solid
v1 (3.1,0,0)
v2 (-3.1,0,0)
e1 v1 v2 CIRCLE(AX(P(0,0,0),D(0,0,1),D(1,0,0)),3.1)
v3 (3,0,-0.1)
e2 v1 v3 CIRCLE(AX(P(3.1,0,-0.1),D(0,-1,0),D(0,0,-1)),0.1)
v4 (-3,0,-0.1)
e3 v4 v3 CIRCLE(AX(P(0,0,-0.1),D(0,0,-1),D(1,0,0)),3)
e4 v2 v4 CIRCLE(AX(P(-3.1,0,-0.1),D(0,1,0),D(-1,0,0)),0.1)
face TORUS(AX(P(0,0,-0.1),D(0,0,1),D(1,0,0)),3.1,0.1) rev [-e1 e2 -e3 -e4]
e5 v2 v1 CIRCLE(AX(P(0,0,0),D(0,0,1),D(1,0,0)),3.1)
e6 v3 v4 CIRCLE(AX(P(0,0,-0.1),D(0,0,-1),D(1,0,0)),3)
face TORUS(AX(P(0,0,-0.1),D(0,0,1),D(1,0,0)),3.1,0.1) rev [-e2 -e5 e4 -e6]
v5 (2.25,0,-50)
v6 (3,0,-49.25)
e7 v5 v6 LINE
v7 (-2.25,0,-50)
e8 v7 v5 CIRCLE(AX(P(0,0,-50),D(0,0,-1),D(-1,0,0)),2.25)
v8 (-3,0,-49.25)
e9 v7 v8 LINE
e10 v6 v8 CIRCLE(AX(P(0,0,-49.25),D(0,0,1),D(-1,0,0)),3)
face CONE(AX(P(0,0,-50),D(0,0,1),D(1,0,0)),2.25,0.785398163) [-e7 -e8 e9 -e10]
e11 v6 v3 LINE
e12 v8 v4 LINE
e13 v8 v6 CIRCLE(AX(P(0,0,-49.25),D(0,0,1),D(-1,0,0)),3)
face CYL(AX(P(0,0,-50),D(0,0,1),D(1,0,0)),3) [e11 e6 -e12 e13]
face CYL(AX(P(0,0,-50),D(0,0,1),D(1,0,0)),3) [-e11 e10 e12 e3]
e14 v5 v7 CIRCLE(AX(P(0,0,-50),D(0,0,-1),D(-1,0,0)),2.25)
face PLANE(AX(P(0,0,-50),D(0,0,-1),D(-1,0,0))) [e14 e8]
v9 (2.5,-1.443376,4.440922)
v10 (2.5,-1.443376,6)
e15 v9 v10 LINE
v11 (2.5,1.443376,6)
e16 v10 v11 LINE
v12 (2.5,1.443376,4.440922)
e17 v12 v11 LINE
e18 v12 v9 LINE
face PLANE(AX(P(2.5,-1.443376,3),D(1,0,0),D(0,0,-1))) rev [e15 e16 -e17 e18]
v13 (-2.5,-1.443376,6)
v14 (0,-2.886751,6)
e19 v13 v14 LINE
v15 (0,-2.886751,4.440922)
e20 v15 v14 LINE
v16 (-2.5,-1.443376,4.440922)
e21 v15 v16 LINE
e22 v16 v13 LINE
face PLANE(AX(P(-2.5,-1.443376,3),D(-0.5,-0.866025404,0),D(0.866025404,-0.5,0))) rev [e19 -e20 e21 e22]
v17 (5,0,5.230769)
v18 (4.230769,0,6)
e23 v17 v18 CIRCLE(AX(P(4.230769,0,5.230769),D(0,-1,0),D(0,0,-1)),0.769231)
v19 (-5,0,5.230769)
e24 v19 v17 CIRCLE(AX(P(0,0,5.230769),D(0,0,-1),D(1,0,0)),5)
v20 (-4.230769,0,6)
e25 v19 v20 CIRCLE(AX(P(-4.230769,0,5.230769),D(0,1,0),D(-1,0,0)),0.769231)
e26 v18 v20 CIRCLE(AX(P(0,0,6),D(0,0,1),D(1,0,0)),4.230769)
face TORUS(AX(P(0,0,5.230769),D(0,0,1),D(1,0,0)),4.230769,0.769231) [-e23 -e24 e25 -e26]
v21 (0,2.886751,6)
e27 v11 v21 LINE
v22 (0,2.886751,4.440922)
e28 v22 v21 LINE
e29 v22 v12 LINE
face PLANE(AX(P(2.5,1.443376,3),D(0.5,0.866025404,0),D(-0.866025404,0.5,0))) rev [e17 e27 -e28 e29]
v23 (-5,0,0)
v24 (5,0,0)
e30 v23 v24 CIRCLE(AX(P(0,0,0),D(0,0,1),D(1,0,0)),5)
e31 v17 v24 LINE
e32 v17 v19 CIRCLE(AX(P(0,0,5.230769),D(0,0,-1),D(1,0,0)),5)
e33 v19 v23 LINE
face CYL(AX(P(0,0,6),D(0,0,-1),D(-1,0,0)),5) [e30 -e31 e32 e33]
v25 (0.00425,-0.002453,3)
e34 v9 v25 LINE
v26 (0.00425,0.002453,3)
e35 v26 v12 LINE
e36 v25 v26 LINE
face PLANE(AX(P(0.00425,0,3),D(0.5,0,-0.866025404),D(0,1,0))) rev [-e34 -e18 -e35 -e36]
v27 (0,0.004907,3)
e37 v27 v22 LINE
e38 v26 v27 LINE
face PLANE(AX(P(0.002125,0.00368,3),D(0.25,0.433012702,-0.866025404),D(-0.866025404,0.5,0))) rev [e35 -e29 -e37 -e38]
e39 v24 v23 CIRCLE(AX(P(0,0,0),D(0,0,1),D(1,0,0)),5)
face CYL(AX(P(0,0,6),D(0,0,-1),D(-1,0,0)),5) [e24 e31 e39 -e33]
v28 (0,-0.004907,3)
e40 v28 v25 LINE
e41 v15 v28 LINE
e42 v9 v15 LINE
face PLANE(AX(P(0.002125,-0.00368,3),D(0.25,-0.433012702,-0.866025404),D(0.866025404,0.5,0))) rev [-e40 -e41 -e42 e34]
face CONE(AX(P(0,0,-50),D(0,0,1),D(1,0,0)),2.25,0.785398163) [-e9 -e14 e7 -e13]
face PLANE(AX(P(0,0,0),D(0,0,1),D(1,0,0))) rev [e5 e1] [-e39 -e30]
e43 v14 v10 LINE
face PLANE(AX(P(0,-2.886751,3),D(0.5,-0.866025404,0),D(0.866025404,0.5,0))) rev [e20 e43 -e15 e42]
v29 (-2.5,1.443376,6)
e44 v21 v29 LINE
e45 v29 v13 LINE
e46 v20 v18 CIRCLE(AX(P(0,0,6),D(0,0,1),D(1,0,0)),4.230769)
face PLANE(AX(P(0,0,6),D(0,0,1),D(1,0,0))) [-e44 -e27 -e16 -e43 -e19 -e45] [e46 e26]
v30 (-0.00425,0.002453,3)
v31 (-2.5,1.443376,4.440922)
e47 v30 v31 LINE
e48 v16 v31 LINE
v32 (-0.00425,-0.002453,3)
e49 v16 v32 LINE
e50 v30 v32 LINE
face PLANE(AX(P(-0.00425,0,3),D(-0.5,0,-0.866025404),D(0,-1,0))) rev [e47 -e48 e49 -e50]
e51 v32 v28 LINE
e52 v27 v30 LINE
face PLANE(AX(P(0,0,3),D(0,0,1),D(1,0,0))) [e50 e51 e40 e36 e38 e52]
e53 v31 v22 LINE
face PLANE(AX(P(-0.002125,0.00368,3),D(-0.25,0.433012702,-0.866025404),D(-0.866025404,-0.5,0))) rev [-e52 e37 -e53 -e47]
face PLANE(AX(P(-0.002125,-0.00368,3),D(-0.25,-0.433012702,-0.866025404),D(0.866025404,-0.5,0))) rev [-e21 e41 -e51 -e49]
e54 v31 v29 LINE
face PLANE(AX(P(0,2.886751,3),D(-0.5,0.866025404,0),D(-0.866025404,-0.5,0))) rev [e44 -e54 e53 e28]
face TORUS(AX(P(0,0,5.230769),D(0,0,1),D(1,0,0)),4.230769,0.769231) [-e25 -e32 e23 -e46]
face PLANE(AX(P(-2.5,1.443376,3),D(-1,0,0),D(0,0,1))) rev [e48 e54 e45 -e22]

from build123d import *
from OCP.BRepFilletAPI import BRepFilletAPI_MakeChamfer

# Parameters (mm, degrees)
SKETCH1_R           = 5
BOSS_EXTRUDE1_DEPTH = 6
CUT_EXTRUDE1_DEPTH  = 3
SKETCH3_R           = 3
BOSS_EXTRUDE2_DEPTH = 50
CHAMFER1_SIZE       = 0.75
FILLET1_R           = 0.769230769
CHAMFER2_SIZE       = 1.44092219
CHAMFER2_SIZE2      = 2.495750443
FILLET2_R           = 0.1


with BuildPart() as part:
    # Sketch1 → Boss-Extrude1 (new body)
    with BuildSketch(Plane.XY):
        Circle(SKETCH1_R)
    extrude(amount=BOSS_EXTRUDE1_DEPTH)

    # Sketch2 → Cut-Extrude1 (cut)
    with BuildSketch(Plane.XY.offset(6)):
        Polygon((2.5, 1.443375673), (0, 2.886751346), (-2.5, 1.443375673), (-2.5, -1.443375673), (0, -2.886751346), (2.5, -1.443375673), align=None)
    extrude(amount=-CUT_EXTRUDE1_DEPTH, mode=Mode.SUBTRACT)

    # Sketch3 → Boss-Extrude2 (add)
    with BuildSketch(Plane(origin=(0, 0, 0), x_dir=(-1, 0, 0), z_dir=(0, 0, -1))):
        with Locations(Location((0, 0, 0), (0, 0, 180))):
            Circle(SKETCH3_R)
    extrude(amount=BOSS_EXTRUDE2_DEPTH)

    # Chamfer1
    chamfer1_edges = [part.edges().sort_by_distance(p)[0] for p in [
        (-3, 0, -50),
    ]]
    chamfer(chamfer1_edges, length=CHAMFER1_SIZE)

    # Fillet1
    fillet1_edges = [part.edges().sort_by_distance(p)[0] for p in [
        (-5, 0, 6),
    ]]
    fillet(fillet1_edges, radius=FILLET1_R)

    # Chamfer2: one chamfer whose edges measure the first distance from different faces: ONE call of the kernel's chamfer builder (chamfer() names one face for all edges)
    chamfer2_edges_1 = [part.edges().sort_by_distance(p)[0] for p in [
        (-1.25, 2.165063509, 3),
    ]]
    chamfer2_side_1 = [part.faces().sort_by_distance(p)[0] for p in [
        (-1.25, 2.165063509, 4.5),
    ]]
    chamfer2_edges_2 = [part.edges().sort_by_distance(p)[0] for p in [
        (1.25, 2.165063509, 3),
    ]]
    chamfer2_side_2 = [part.faces().sort_by_distance(p)[0] for p in [
        (1.25, 2.165063509, 4.5),
    ]]
    chamfer2_edges_3 = [part.edges().sort_by_distance(p)[0] for p in [
        (2.5, 0, 3),
    ]]
    chamfer2_side_3 = [part.faces().sort_by_distance(p)[0] for p in [
        (2.5, 0, 4.5),
    ]]
    chamfer2_edges_4 = [part.edges().sort_by_distance(p)[0] for p in [
        (1.25, -2.165063509, 3),
    ]]
    chamfer2_side_4 = [part.faces().sort_by_distance(p)[0] for p in [
        (1.25, -2.165063509, 4.5),
    ]]
    chamfer2_edges_5 = [part.edges().sort_by_distance(p)[0] for p in [
        (-1.25, -2.165063509, 3),
    ]]
    chamfer2_side_5 = [part.faces().sort_by_distance(p)[0] for p in [
        (-1.25, -2.165063509, 4.5),
    ]]
    chamfer2_edges_6 = [part.edges().sort_by_distance(p)[0] for p in [
        (-2.5, 0, 3),
    ]]
    chamfer2_side_6 = [part.faces().sort_by_distance(p)[0] for p in [
        (-2.5, 0, 4.5),
    ]]
    chamfer2 = BRepFilletAPI_MakeChamfer(part.part.solid().wrapped)
    for e in chamfer2_edges_1:
        chamfer2.Add(CHAMFER2_SIZE, CHAMFER2_SIZE2, e.wrapped, chamfer2_side_1[0].wrapped)  # the first distance lies on this face
    for e in chamfer2_edges_2:
        chamfer2.Add(CHAMFER2_SIZE, CHAMFER2_SIZE2, e.wrapped, chamfer2_side_2[0].wrapped)  # the first distance lies on this face
    for e in chamfer2_edges_3:
        chamfer2.Add(CHAMFER2_SIZE, CHAMFER2_SIZE2, e.wrapped, chamfer2_side_3[0].wrapped)  # the first distance lies on this face
    for e in chamfer2_edges_4:
        chamfer2.Add(CHAMFER2_SIZE, CHAMFER2_SIZE2, e.wrapped, chamfer2_side_4[0].wrapped)  # the first distance lies on this face
    for e in chamfer2_edges_5:
        chamfer2.Add(CHAMFER2_SIZE, CHAMFER2_SIZE2, e.wrapped, chamfer2_side_5[0].wrapped)  # the first distance lies on this face
    for e in chamfer2_edges_6:
        chamfer2.Add(CHAMFER2_SIZE, CHAMFER2_SIZE2, e.wrapped, chamfer2_side_6[0].wrapped)  # the first distance lies on this face
    add(Compound.cast(chamfer2.Shape()), mode=Mode.REPLACE)

    # Fillet2
    fillet2_edges = [part.edges().sort_by_distance(p)[0] for p in [
        (-3, 0, 0),
    ]]
    fillet(fillet2_edges, radius=FILLET2_R)


solid = part.part
